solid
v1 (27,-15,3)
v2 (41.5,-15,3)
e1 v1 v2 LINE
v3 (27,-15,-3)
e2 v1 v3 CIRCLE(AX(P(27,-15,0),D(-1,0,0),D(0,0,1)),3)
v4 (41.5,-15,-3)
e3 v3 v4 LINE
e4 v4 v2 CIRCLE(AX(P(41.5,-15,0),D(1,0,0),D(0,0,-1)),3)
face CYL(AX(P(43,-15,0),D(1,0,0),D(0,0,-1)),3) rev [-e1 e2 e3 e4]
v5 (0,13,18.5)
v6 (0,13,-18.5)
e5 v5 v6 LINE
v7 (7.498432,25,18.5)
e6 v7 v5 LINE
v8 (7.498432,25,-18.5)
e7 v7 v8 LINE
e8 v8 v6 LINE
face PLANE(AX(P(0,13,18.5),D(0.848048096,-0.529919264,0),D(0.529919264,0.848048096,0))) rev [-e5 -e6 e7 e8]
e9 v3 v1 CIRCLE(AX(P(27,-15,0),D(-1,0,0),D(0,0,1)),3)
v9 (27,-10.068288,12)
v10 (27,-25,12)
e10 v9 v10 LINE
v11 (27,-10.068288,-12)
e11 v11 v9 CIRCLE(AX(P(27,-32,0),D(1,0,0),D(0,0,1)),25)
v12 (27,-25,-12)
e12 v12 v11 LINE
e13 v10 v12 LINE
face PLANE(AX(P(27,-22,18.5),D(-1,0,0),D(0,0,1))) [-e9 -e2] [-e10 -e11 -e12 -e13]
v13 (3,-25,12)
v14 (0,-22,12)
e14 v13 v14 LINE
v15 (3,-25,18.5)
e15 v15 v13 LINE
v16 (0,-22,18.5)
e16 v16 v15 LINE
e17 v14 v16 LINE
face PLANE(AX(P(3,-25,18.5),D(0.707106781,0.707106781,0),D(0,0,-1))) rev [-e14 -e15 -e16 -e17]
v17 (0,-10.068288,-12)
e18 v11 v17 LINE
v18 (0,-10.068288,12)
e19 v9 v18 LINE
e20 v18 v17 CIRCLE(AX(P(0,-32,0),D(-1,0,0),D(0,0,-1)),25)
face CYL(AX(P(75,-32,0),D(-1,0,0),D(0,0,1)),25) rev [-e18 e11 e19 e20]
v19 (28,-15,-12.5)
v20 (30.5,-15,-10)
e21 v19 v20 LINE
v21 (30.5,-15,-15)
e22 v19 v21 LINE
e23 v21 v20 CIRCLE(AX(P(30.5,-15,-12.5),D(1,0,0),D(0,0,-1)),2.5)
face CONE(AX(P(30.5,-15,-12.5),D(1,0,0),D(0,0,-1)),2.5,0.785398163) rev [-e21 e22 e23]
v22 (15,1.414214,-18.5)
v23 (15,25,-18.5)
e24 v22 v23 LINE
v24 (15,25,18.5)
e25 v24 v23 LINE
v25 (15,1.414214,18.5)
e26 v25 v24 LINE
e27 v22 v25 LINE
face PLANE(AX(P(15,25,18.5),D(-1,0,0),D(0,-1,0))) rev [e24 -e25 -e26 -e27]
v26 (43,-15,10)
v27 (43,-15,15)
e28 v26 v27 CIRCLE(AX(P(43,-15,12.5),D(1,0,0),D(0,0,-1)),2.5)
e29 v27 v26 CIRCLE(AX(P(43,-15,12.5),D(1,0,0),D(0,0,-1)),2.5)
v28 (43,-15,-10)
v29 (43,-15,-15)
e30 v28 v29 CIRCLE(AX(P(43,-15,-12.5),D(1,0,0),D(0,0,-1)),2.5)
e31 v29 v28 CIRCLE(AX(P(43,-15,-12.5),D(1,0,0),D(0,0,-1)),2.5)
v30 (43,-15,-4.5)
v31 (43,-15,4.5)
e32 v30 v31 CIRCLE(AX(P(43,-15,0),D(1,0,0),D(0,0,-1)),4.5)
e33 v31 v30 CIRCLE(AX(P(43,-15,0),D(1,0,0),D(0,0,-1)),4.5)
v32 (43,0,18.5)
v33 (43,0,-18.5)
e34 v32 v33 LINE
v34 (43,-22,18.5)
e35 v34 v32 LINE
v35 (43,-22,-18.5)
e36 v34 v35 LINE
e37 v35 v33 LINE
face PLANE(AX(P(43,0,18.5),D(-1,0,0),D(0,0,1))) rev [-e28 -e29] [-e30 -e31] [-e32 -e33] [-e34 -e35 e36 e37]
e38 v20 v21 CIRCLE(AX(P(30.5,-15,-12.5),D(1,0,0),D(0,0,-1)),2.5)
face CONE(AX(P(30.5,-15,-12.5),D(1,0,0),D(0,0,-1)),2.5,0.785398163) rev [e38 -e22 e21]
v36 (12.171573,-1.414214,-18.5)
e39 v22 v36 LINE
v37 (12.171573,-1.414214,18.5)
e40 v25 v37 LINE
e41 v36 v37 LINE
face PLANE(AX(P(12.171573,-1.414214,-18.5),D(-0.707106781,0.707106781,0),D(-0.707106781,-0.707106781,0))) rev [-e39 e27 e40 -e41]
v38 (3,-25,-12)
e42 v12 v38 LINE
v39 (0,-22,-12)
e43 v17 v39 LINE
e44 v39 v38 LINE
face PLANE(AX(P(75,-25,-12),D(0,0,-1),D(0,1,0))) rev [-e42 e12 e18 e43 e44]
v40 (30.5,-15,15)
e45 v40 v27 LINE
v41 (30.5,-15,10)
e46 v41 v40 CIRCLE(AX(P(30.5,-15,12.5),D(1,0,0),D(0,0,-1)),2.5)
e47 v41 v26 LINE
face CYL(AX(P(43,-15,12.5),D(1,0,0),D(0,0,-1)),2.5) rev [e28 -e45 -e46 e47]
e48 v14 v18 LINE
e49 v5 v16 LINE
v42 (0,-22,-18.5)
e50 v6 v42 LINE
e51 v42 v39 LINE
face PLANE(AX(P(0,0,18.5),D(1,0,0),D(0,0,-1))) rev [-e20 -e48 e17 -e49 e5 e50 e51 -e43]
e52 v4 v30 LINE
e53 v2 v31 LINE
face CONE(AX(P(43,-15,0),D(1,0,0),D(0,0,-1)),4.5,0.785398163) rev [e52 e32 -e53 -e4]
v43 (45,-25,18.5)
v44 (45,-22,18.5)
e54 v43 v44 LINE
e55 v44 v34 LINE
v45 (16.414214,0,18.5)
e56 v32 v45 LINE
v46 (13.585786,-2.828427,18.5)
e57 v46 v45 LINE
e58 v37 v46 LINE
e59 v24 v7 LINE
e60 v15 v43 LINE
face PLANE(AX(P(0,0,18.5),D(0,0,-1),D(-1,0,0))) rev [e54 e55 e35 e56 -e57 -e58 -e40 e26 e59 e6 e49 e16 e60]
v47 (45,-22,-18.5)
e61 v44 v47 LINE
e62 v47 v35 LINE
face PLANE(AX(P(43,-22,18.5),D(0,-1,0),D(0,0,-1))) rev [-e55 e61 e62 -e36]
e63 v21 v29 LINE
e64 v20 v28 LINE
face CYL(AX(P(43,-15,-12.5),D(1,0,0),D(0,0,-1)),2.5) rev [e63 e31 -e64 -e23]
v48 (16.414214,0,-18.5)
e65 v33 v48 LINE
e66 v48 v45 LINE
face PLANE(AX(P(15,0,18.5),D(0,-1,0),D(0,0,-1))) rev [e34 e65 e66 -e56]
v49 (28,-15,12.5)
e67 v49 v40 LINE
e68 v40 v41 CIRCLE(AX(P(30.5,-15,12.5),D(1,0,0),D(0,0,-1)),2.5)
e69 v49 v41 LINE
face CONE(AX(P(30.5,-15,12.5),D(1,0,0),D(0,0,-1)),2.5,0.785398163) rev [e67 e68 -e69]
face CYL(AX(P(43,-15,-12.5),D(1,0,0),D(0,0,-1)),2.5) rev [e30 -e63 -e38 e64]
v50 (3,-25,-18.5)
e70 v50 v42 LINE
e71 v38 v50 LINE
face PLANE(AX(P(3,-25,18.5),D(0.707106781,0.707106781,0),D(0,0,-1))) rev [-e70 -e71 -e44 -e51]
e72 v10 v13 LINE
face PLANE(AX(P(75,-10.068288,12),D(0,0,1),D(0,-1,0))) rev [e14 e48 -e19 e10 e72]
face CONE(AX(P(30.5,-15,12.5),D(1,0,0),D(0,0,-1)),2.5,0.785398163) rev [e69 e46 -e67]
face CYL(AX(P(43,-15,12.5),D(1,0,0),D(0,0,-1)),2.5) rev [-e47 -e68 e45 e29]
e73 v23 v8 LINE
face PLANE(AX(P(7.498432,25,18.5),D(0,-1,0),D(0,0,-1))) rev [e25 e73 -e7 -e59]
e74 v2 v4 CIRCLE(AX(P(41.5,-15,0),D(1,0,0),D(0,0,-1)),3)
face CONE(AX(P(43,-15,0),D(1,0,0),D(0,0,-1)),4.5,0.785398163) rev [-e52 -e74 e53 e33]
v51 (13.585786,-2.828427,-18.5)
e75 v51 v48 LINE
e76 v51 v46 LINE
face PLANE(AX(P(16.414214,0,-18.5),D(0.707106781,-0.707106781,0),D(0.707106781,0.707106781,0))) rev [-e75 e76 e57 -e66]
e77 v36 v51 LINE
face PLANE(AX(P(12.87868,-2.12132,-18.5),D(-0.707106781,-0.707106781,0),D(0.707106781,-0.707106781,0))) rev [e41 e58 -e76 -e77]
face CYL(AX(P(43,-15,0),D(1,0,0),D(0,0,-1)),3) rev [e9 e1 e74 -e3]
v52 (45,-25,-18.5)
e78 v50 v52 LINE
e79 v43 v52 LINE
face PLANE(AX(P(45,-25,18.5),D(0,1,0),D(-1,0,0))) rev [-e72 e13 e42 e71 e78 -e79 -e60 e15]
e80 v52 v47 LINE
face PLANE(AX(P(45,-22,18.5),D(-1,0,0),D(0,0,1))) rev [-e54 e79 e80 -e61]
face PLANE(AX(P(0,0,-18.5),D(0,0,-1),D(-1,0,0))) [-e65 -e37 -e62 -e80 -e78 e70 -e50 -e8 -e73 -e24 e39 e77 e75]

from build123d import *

# Parameters (mm, degrees)
ANCHOR_BLOCK_BODY_DEPTH             = 18.5
TOP_EDGE_CHAMFER_3X45_SIZE          = 3
STEP_GROOVE_DEPTH                   = 64.395583442
STEP_CUT_18_DEEP_DEPTH              = 27
COUNTERSUNK_THRU_HOLE_6_D           = 6
COUNTERSUNK_THRU_HOLE_6_CSINK_D     = 9
COUNTERSUNK_THRU_HOLE_6_CSINK_ANGLE = 90
DRILLED_HOLES_5X15_D                = 5
DRILLED_HOLES_5X15_DEPTH            = 12.5
DRILLED_HOLES_5X15_TIP              = 2.5


with BuildPart() as part:
    # Block Profile Sketch → Anchor Block Body (new, symmetric)
    with BuildSketch(Plane.XY):
        Polygon((0, 0), (0, 13), (7.498432223, 25), (15, 25), (15, 0), (43, 0), (43, -22), (45, -22), (45, -25), (0, -25), align=None)
    extrude(amount=ANCHOR_BLOCK_BODY_DEPTH, both=True)

    # Top Edge Chamfer 3x45
    top_edge_chamfer_3x45_edges = [part.edges().sort_by_distance(p)[0] for p in [
        (0, -25, 0),
    ]]
    chamfer(top_edge_chamfer_3x45_edges, length=TOP_EDGE_CHAMFER_3X45_SIZE)

    # Step Groove Sketch → Step Groove (cut, through all)
    with BuildSketch(Plane.XY.offset(18.5)):
        Polygon((12.878679656, -2.121320344), (12.171572875, -1.414213562), (15, 1.414213562), (16.414213562, 0), (13.585786438, -2.828427125), align=None)
    extrude(amount=-STEP_GROOVE_DEPTH, mode=Mode.SUBTRACT)

    # Step Cut Sketch → Step Cut 18 Deep (cut)
    with BuildSketch(Plane.ZY):
        with BuildLine():
            Line((-12, -25), (-12, -10.068287801))
            ThreePointArc((-12, -10.068287801), (0, -7), (12, -10.068287801))
            Line((12, -10.068287801), (12, -25))
            Line((12, -25), (-12, -25))
        make_face()
    extrude(amount=-STEP_CUT_18_DEEP_DEPTH, mode=Mode.SUBTRACT)

    # Countersunk Thru Hole Ø6 (through all)
    with Locations(Plane(origin=(43, 0, 0), x_dir=(0, 0, -1), z_dir=(1, 0, 0))):
        with Locations((0, -15)):
            CounterSinkHole(COUNTERSUNK_THRU_HOLE_6_D / 2, COUNTERSUNK_THRU_HOLE_6_CSINK_D / 2, counter_sink_angle=COUNTERSUNK_THRU_HOLE_6_CSINK_ANGLE)

    # Drilled Holes Ø5x15
    with Locations(Plane(origin=(43, 0, 0), x_dir=(0, 0, -1), z_dir=(1, 0, 0))):
        with Locations((12.5, -15), (-12.5, -15)):
            Hole(DRILLED_HOLES_5X15_D / 2, depth=DRILLED_HOLES_5X15_DEPTH)
            with Locations((0, 0, -(DRILLED_HOLES_5X15_DEPTH + DRILLED_HOLES_5X15_TIP / 2))):  # 90° drill point
                Cone(0, DRILLED_HOLES_5X15_D / 2, DRILLED_HOLES_5X15_TIP, mode=Mode.SUBTRACT)


solid = part.part
